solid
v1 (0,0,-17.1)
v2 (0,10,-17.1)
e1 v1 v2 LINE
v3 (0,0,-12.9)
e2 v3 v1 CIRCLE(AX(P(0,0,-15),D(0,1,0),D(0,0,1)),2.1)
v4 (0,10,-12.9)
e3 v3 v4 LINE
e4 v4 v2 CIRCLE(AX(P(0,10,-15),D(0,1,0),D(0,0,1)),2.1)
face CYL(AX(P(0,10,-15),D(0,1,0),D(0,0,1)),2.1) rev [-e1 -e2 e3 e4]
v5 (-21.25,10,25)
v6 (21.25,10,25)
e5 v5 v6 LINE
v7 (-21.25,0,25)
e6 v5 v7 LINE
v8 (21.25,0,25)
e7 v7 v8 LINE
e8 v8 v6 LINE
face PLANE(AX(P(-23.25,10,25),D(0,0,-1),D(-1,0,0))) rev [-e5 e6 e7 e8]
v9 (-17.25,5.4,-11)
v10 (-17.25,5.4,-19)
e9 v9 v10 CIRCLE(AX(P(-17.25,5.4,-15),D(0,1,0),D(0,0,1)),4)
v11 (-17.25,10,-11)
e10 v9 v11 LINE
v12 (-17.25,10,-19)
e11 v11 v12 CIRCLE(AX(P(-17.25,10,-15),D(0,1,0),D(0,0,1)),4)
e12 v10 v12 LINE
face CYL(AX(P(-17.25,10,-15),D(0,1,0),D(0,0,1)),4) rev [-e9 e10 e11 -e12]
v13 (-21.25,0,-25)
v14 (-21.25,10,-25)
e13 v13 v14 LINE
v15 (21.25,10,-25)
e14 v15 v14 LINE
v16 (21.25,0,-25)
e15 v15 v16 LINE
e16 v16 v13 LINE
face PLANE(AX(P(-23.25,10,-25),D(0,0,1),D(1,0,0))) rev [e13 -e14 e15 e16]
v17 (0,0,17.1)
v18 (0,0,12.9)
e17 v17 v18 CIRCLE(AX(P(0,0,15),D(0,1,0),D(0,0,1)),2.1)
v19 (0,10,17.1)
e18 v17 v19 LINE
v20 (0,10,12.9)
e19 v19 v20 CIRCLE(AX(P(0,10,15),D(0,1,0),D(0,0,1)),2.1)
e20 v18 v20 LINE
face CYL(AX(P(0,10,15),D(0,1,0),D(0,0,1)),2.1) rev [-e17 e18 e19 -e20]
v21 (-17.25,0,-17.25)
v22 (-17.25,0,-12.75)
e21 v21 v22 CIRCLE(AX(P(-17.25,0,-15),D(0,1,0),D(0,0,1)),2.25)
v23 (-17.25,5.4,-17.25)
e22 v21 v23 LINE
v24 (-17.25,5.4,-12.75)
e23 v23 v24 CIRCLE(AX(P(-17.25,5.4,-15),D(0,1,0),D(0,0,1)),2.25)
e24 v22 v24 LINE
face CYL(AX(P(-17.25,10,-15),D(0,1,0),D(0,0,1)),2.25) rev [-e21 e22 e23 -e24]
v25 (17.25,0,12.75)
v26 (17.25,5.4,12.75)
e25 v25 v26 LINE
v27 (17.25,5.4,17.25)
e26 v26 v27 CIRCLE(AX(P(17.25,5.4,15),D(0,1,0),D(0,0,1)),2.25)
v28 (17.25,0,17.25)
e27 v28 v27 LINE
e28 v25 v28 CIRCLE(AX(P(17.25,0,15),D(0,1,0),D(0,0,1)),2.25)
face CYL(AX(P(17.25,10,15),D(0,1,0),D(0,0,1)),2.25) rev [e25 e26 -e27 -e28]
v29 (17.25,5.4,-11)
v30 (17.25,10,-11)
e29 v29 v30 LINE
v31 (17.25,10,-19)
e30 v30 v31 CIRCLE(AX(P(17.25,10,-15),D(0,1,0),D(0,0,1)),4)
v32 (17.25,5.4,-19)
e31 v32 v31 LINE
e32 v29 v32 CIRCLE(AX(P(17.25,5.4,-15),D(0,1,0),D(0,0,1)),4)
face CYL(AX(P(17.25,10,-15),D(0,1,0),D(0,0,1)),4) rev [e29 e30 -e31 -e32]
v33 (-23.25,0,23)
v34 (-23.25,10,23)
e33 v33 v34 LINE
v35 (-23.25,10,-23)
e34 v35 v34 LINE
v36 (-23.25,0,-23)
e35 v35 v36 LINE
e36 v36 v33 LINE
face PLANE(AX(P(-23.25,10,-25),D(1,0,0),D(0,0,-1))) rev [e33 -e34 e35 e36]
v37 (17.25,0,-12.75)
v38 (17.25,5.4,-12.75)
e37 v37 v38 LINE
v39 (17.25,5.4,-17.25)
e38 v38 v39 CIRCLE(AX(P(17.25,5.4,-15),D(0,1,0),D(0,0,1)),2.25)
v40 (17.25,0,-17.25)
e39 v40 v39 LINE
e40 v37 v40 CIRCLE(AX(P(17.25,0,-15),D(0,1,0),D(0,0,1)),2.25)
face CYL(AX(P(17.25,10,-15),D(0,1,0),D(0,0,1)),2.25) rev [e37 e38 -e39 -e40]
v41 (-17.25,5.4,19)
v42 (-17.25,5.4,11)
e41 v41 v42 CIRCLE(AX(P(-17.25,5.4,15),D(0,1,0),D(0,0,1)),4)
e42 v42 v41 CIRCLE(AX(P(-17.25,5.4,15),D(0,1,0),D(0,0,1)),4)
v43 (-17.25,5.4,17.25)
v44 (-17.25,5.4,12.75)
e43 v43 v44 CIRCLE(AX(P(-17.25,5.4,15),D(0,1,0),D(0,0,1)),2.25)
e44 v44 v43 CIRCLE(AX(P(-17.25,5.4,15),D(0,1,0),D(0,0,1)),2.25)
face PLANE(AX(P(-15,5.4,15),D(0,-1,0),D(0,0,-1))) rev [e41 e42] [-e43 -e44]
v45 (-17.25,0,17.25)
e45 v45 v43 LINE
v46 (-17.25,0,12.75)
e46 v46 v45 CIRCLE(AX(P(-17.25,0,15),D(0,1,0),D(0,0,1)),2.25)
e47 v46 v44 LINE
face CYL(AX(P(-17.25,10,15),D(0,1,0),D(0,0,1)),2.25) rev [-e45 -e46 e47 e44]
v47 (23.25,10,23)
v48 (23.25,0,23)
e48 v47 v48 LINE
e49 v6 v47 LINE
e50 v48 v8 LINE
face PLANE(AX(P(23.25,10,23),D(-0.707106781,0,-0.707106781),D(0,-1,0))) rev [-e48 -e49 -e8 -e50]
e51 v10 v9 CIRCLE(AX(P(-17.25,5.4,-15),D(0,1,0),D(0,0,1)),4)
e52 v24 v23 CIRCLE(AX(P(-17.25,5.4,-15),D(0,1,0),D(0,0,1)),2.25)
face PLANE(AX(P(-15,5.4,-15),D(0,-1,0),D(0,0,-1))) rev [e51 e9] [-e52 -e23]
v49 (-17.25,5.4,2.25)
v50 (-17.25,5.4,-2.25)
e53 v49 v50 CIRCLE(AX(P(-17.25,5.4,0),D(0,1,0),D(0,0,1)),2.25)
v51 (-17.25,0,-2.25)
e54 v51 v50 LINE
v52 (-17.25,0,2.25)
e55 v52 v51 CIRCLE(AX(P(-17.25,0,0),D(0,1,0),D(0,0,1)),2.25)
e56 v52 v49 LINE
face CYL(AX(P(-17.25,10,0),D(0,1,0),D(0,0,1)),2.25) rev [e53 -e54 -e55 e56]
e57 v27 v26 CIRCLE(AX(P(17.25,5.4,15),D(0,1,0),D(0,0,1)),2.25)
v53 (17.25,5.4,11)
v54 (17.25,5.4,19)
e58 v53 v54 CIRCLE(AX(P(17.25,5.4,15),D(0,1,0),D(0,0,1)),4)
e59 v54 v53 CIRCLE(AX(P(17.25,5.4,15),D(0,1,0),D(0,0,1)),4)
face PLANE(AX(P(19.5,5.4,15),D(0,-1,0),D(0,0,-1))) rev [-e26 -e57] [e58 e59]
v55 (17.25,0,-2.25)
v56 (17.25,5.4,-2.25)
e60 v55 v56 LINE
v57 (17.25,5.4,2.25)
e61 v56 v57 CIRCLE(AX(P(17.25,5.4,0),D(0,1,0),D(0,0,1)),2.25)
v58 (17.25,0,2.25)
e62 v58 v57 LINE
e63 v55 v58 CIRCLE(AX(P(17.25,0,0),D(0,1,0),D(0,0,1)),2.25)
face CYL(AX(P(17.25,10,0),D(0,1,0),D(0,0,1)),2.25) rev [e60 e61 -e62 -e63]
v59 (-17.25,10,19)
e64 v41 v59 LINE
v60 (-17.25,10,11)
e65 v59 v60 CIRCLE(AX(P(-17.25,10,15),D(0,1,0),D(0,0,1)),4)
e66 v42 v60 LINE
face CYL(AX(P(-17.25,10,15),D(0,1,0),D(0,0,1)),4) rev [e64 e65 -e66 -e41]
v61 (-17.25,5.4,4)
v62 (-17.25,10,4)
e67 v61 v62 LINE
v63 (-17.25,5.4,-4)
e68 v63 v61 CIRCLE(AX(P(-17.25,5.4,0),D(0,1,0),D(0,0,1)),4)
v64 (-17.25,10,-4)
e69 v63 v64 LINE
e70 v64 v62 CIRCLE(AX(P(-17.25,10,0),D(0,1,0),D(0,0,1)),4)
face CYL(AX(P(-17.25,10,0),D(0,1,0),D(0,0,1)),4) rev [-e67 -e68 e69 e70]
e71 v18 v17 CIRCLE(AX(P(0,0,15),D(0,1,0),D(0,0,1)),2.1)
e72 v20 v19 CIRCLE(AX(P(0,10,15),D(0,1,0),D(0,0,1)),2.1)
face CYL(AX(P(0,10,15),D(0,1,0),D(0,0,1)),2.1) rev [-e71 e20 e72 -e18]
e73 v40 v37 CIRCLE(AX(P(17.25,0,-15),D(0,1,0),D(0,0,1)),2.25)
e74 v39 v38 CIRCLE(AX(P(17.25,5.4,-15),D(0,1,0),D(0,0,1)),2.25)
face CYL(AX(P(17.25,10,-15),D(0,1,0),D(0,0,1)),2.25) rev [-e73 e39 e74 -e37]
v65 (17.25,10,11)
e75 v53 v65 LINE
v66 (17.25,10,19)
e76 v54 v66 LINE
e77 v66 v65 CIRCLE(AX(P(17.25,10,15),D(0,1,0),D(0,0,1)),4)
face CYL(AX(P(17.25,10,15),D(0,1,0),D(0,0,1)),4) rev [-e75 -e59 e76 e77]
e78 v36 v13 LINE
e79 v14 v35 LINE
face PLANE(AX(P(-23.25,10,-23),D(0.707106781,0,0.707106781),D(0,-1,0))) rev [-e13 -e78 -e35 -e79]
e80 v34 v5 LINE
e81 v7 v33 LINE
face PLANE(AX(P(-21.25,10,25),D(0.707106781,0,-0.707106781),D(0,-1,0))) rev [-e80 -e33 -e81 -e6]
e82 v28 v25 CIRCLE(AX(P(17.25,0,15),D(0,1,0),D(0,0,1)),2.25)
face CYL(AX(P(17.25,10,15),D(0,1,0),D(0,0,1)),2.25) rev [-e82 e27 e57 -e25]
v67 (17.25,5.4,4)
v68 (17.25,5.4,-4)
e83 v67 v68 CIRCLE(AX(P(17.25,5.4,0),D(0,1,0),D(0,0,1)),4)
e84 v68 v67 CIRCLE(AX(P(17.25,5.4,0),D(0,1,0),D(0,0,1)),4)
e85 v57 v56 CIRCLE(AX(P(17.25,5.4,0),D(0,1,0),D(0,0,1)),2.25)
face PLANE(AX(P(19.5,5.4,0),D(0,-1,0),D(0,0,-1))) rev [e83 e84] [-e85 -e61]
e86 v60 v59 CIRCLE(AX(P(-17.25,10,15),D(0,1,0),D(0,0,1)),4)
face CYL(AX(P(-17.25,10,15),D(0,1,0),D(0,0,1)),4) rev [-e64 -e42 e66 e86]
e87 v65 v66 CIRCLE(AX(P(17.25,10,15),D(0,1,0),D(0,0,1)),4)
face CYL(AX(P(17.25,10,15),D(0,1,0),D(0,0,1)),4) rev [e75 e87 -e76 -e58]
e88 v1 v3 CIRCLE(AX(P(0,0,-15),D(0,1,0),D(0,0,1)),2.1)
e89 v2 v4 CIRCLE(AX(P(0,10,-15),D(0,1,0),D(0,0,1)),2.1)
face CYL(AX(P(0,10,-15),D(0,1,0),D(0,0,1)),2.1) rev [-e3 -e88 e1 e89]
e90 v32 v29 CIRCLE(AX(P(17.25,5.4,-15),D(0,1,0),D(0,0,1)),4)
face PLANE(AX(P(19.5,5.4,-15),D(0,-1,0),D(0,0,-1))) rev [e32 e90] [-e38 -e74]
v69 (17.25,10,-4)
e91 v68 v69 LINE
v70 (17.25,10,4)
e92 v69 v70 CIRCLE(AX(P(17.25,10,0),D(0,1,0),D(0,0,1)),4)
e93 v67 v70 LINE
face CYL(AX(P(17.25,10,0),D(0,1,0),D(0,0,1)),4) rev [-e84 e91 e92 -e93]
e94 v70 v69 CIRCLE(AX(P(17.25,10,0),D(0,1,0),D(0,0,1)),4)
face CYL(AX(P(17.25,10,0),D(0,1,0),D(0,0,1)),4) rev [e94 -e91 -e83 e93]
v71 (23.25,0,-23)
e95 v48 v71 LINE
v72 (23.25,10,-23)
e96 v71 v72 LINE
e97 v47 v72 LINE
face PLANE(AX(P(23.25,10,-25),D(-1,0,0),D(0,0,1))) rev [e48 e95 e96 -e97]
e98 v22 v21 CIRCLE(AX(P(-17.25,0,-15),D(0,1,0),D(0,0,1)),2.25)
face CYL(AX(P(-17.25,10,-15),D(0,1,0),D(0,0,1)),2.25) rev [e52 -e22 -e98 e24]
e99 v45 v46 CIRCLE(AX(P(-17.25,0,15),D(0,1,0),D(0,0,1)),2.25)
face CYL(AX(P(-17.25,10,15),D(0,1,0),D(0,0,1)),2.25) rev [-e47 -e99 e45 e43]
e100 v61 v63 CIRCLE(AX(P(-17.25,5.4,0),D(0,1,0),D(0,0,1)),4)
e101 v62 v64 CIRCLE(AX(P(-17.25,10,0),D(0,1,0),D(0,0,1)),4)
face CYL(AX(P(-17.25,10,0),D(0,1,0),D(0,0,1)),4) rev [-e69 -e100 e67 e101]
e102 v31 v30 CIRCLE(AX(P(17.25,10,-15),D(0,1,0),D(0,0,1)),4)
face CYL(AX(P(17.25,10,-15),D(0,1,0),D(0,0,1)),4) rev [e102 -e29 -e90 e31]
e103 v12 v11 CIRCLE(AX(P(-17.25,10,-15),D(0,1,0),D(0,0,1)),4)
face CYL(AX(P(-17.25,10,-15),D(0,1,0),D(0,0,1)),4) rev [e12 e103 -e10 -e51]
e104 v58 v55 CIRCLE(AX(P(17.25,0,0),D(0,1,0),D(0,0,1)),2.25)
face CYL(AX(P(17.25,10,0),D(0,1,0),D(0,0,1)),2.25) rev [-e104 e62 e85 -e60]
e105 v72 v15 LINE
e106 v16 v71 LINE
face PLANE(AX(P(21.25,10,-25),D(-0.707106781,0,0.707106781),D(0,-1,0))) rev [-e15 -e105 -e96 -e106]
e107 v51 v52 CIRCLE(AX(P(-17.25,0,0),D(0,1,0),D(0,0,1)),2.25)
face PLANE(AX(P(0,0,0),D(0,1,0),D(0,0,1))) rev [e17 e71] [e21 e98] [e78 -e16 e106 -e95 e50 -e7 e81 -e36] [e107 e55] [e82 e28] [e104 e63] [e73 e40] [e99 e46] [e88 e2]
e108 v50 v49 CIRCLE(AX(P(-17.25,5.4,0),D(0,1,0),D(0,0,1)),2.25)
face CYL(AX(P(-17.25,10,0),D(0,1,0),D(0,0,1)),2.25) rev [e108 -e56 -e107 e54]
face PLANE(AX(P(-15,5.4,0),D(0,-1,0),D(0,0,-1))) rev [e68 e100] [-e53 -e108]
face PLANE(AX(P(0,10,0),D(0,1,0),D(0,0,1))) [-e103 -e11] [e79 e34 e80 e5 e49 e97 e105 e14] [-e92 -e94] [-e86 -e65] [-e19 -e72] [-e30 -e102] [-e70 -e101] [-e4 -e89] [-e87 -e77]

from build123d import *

# Parameters (mm, degrees)
SKETCH_1_W                = 46.5
SKETCH_1_H                = 50
EXTRUDE_1_DEPTH           = 10
HOLE_WIZARD_1_D           = 4.5
HOLE_WIZARD_1_DEPTH       = 20
HOLE_WIZARD_1_CBORE_D     = 8
HOLE_WIZARD_1_CBORE_DEPTH = 4.6
HOLE_WIZARD_1_TIP         = 1.351936393
CHAMFER_1_SIZE            = 2
HOLE_WIZARD_M5_1_D        = 4.2


with BuildPart() as part:
    # 草图1 → 凸台-拉伸1 (new body)
    with BuildSketch(Plane(origin=(0, 0, 0), x_dir=(1, 0, 0), z_dir=(0, 1, 0))):
        Rectangle(SKETCH_1_W, SKETCH_1_H)
    extrude(amount=EXTRUDE_1_DEPTH)

    # 打孔尺寸(%根据)内六角圆柱头螺钉的类型1
    with Locations(Plane(origin=(0, 10, 0), x_dir=(1, 0, 0), z_dir=(0, 1, 0))):
        with Locations((17.25, -15), (17.25, 0), (17.25, 15), (-17.25, 15), (-17.25, 0), (-17.25, -15)):
            CounterBoreHole(HOLE_WIZARD_1_D / 2, HOLE_WIZARD_1_CBORE_D / 2, HOLE_WIZARD_1_CBORE_DEPTH, depth=HOLE_WIZARD_1_DEPTH)
            with Locations((0, 0, -(HOLE_WIZARD_1_DEPTH + HOLE_WIZARD_1_TIP / 2))):  # 118° drill point
                Cone(0, HOLE_WIZARD_1_D / 2, HOLE_WIZARD_1_TIP, mode=Mode.SUBTRACT)

    # 倒角1
    chamfer_1_edges = [part.edges().sort_by_distance(p)[0] for p in [
        (23.25, 5, 25),
        (-23.25, 5, 25),
        (-23.25, 5, -25),
        (23.25, 5, -25),
    ]]
    chamfer(chamfer_1_edges, length=CHAMFER_1_SIZE)

    # M5 螺纹孔1 (through all)
    with Locations(Plane(origin=(0, 10, 0), x_dir=(1, 0, 0), z_dir=(0, 1, 0))):
        with Locations((0, 15), (0, -15)):
            Hole(HOLE_WIZARD_M5_1_D / 2)


solid = part.part
